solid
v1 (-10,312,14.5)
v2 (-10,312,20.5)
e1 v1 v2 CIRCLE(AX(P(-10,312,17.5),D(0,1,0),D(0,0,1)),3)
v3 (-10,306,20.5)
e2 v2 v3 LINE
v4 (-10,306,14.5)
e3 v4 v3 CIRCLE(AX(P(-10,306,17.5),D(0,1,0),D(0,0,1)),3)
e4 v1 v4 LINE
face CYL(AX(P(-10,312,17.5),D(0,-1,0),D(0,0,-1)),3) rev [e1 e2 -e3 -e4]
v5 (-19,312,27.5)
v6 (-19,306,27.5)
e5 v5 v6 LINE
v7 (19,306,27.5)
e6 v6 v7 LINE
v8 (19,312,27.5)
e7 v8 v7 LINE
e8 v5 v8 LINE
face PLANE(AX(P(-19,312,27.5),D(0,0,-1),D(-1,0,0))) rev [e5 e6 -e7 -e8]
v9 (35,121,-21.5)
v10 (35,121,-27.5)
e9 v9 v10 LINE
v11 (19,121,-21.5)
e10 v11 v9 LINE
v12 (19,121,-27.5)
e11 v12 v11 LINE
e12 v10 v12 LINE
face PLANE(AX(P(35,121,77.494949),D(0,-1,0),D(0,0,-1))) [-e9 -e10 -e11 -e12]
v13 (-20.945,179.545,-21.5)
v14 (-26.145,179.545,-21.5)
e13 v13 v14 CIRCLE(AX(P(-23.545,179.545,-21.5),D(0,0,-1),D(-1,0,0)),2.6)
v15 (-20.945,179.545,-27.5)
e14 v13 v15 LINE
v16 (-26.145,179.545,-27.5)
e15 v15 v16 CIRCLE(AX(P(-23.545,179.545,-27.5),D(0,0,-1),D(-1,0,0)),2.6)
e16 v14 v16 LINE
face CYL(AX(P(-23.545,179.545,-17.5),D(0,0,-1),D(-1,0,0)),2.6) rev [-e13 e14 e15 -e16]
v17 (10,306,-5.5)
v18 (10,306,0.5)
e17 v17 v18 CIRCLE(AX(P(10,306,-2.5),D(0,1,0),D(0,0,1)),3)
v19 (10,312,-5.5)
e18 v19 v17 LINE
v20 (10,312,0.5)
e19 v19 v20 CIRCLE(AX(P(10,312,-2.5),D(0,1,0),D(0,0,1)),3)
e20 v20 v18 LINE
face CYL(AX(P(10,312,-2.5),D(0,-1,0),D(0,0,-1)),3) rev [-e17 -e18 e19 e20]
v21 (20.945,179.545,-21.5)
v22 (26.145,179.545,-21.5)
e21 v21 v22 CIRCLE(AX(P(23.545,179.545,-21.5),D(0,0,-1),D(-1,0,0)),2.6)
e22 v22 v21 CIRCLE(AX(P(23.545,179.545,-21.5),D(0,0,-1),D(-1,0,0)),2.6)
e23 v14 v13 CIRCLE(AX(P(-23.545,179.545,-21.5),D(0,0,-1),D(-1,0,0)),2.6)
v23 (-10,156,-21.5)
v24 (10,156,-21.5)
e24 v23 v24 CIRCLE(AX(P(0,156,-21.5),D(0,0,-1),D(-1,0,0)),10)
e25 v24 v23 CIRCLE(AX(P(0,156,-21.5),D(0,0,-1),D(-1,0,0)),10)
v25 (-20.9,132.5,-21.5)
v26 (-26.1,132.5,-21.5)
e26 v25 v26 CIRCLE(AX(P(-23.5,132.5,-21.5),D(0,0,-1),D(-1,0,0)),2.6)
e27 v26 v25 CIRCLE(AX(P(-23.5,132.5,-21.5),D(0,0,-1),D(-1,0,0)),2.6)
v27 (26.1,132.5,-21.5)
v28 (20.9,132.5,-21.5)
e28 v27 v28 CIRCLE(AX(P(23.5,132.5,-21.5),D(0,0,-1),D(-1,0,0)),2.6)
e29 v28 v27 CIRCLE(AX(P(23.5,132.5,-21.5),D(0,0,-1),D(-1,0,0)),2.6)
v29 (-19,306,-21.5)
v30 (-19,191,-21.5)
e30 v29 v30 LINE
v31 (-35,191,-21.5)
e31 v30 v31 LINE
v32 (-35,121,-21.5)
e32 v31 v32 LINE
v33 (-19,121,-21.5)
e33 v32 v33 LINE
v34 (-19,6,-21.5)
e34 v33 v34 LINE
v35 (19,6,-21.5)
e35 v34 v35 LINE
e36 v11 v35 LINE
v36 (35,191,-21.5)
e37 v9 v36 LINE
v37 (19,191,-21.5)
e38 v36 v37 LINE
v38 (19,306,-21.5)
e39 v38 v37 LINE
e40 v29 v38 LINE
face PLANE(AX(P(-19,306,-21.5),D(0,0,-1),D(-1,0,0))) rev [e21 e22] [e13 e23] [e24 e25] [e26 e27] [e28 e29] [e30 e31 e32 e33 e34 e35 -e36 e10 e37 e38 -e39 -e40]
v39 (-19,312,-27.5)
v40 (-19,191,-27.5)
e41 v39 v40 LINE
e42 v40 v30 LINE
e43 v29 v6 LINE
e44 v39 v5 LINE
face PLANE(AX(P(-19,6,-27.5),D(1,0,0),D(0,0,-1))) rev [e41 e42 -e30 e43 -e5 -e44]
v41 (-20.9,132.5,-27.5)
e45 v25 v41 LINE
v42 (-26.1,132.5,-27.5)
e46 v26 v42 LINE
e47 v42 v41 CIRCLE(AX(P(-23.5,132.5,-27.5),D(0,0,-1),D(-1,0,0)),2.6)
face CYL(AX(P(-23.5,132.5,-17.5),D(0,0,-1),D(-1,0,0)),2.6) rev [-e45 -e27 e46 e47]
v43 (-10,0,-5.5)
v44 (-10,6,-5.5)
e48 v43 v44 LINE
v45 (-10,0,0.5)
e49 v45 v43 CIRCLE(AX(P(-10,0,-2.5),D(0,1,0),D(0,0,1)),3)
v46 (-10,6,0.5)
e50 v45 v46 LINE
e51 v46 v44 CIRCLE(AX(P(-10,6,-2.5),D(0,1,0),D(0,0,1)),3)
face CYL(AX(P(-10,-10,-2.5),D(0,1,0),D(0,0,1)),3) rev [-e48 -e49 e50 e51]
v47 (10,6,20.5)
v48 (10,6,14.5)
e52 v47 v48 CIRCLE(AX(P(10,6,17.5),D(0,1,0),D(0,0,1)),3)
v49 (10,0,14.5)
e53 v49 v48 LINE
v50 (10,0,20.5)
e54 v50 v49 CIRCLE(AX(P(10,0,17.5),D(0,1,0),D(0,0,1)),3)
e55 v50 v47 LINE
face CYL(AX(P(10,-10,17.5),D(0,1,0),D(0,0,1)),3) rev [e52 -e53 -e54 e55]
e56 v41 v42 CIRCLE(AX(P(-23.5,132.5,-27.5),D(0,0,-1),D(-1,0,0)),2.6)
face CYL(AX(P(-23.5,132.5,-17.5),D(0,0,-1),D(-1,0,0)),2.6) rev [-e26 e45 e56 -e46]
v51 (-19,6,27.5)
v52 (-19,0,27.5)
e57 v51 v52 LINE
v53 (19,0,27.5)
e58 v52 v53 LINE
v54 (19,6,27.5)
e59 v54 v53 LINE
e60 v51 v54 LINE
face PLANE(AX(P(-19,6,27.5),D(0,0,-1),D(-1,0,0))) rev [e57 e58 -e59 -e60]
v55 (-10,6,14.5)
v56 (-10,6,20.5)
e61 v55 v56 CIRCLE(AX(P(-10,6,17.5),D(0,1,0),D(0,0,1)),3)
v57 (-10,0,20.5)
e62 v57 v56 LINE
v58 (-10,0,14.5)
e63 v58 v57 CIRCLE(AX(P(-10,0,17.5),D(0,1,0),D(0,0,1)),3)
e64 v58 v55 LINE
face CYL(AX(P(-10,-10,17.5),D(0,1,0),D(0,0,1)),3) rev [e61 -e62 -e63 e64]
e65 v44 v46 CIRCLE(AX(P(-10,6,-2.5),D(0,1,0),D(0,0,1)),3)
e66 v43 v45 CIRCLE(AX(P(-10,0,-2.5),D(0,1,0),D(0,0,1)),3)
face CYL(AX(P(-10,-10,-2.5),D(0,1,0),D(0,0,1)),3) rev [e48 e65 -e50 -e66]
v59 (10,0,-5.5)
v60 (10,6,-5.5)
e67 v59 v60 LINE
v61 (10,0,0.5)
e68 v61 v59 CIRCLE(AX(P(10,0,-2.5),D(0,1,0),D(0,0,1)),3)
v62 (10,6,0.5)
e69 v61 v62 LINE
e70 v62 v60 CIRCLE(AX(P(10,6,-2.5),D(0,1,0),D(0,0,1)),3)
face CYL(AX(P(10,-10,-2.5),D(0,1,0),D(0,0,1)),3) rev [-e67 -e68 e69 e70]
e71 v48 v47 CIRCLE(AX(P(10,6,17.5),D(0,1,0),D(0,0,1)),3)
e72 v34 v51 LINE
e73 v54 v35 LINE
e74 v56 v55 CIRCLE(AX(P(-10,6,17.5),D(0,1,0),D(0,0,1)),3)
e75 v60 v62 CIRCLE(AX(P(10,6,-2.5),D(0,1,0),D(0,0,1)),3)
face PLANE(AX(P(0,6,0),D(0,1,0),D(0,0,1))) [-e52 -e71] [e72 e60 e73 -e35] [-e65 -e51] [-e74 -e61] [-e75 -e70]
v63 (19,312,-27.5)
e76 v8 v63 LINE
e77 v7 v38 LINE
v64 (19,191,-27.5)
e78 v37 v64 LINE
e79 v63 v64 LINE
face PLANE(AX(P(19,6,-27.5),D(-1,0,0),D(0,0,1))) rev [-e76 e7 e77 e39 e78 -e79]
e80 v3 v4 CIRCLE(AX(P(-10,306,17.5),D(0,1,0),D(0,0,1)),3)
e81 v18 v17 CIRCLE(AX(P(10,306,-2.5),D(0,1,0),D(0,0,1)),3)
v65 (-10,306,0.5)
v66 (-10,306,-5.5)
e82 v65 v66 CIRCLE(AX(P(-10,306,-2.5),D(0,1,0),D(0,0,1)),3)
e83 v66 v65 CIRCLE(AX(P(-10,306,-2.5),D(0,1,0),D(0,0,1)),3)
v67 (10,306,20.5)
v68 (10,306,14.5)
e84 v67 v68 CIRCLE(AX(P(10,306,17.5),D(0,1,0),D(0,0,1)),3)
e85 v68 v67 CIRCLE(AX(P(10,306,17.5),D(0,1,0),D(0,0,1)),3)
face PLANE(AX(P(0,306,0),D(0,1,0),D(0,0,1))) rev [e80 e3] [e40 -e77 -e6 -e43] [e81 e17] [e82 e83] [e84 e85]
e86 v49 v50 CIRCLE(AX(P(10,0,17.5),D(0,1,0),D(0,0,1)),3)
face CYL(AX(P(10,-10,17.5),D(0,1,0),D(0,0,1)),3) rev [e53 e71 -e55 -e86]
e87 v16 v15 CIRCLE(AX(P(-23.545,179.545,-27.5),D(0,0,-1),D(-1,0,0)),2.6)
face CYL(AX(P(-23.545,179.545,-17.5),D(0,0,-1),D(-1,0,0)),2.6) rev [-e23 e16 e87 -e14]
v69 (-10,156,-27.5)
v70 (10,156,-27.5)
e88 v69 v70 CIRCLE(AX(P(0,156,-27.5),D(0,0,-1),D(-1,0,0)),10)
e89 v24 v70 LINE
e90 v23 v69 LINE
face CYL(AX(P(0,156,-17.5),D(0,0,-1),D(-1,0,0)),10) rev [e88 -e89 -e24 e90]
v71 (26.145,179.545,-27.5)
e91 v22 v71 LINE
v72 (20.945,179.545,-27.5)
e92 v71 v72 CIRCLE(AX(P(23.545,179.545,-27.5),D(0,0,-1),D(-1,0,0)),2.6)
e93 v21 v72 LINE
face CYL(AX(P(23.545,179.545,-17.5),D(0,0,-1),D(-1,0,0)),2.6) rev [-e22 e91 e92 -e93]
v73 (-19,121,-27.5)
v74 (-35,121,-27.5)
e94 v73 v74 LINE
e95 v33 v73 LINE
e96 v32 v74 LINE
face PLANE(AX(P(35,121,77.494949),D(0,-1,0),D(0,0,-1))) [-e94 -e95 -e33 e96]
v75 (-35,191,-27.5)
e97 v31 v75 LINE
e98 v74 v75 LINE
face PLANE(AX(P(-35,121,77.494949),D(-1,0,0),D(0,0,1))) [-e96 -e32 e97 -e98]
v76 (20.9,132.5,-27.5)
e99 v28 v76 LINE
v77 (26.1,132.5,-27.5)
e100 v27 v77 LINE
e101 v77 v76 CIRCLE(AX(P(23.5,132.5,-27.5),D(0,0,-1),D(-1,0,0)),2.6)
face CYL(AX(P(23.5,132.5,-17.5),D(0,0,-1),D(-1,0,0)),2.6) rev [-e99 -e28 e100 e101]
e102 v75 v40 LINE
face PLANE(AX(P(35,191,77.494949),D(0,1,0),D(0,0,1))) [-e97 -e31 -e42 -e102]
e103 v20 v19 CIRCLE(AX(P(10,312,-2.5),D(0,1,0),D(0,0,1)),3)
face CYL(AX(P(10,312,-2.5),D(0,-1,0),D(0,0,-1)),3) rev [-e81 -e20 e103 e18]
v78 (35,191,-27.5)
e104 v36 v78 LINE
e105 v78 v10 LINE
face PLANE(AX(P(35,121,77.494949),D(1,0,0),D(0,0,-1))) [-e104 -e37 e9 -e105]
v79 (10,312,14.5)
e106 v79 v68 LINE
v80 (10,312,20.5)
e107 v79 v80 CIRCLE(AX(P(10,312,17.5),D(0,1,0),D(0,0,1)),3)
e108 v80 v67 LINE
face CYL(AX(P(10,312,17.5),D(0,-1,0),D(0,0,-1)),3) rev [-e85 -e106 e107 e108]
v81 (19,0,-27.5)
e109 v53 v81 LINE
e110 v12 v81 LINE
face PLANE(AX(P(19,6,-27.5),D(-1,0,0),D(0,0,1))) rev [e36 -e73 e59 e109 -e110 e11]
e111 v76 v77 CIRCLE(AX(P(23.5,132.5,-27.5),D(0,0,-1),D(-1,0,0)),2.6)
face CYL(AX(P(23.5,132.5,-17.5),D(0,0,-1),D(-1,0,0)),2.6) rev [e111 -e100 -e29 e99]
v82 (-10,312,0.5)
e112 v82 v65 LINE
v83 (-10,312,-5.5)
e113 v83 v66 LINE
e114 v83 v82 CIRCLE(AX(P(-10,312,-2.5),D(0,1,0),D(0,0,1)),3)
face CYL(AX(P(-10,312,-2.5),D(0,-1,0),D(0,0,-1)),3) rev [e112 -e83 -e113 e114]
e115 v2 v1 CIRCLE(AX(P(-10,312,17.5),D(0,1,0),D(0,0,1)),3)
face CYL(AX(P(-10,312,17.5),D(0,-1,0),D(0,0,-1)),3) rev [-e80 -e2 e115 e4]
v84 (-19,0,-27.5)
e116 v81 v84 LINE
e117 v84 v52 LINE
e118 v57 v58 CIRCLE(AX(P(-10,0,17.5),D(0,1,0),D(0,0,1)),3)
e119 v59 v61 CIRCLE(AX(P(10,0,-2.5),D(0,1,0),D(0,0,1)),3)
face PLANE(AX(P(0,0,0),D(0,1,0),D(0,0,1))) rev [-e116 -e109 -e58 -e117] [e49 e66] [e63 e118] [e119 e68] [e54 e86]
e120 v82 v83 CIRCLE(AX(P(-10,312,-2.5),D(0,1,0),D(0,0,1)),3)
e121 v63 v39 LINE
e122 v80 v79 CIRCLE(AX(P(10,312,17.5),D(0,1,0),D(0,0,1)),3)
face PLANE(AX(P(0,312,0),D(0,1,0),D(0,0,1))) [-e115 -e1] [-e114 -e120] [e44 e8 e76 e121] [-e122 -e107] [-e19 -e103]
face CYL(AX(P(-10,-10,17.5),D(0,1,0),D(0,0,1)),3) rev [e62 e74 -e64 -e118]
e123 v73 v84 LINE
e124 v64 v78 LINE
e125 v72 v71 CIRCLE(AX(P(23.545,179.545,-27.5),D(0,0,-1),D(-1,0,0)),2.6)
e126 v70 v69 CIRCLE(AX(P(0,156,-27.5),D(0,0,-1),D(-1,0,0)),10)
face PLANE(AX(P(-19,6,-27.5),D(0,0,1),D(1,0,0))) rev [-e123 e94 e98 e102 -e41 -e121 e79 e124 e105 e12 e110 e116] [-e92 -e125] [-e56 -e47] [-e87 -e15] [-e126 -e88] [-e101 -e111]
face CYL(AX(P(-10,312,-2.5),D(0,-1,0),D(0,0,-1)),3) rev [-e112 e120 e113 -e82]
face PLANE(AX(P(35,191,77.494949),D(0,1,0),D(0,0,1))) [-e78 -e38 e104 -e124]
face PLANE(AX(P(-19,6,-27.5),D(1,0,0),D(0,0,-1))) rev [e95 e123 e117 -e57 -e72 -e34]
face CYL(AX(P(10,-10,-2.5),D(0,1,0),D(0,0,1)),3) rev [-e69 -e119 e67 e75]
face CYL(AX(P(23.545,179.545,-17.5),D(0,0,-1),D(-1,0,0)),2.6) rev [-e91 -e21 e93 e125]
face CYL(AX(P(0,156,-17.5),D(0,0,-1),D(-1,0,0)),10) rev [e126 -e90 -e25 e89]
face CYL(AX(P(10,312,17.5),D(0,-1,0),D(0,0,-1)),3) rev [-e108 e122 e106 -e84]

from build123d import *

# Parameters (mm, degrees)
SKETCH_1_W          = 38
SKETCH_1_H          = 55
EXTRUDE_1_DEPTH     = 6
SKETCH_2_R          = 3
CUT_EXTRUDE_1_DEPTH = 16
SKETCH_3_W          = 38
SKETCH_3_H          = 6
EXTRUDE_2_DEPTH     = 300
EXTRUDE_START       = 6
SKETCH_5_R          = 3
EXTRUDE_3_DEPTH     = 6
SKETCH_6_W          = 70
SKETCH_6_H          = 70
EXTRUDE_4_DEPTH     = 6
SKETCH_7_R          = 2.6
SKETCH_7_R_2        = 10
CUT_EXTRUDE_2_DEPTH = 10


with BuildPart() as part:
    # 草图1 → 凸台-拉伸1 (new body)
    with BuildSketch(Plane(origin=(0, 0, 0), x_dir=(1, 0, 0), z_dir=(0, 1, 0))):
        Rectangle(SKETCH_1_W, SKETCH_1_H)
    extrude(amount=EXTRUDE_1_DEPTH)

    # 草图2 → 切除-拉伸1 (cut)
    with BuildSketch(Plane(origin=(0, 6, 0), x_dir=(1, 0, 0), z_dir=(0, 1, 0))):
        with Locations(Location((-10, 2.5, 0), (0, 0, 270))):
            Circle(SKETCH_2_R)
        with Locations(Location((10, 2.5, 0), (0, 0, 270))):
            Circle(SKETCH_2_R)
        with Locations(Location((10, -17.5, 0), (0, 0, 270))):
            Circle(SKETCH_2_R)
        with Locations(Location((-10, -17.5, 0), (0, 0, 270))):
            Circle(SKETCH_2_R)
    extrude(amount=-CUT_EXTRUDE_1_DEPTH, mode=Mode.SUBTRACT)

    # 草图3 → 凸台-拉伸2 (add)
    with BuildSketch(Plane(origin=(0, 6, 0), x_dir=(1, 0, 0), z_dir=(0, 1, 0))):
        with Locations((0, 24.5)):
            Rectangle(SKETCH_3_W, SKETCH_3_H)
    extrude(amount=EXTRUDE_2_DEPTH)

    # 草图5 → 凸台-拉伸3 (add)
    with BuildSketch(Plane(origin=(0, 306, 0), x_dir=(1, 0, 0), z_dir=(0, 1, 0)).offset(EXTRUDE_START)):
        Polygon((-19, 27.5), (-19, 21.5), (-19, -27.5), (19, -27.5), (19, 21.5), (19, 27.5), align=None)
        with Locations(Location((-10, 2.5, 0), (0, 0, 270))):
            Circle(SKETCH_5_R, mode=Mode.SUBTRACT)
        with Locations(Location((10, 2.5, 0), (0, 0, 270))):
            Circle(SKETCH_5_R, mode=Mode.SUBTRACT)
        with Locations(Location((-10, -17.5, 0), (0, 0, 270))):
            Circle(SKETCH_5_R, mode=Mode.SUBTRACT)
        with Locations(Location((10, -17.5, 0), (0, 0, 270))):
            Circle(SKETCH_5_R, mode=Mode.SUBTRACT)
    extrude(amount=-EXTRUDE_3_DEPTH)

    # 草图6 → 凸台-拉伸4 (add)
    with BuildSketch(Plane(origin=(0, 0, -27.5), x_dir=(-1, 0, 0), z_dir=(0, 0, -1))):
        with Locations((0, 156)):
            Rectangle(SKETCH_6_W, SKETCH_6_H)
    extrude(amount=-EXTRUDE_4_DEPTH)

    # 草图7 → 切除-拉伸2 (cut)
    with BuildSketch(Plane(origin=(0, 0, -27.5), x_dir=(-1, 0, 0), z_dir=(0, 0, -1))):
        with Locations((23.545, 179.545)):
            Circle(SKETCH_7_R)
        with Locations((23.5, 132.5)):
            Circle(SKETCH_7_R)
        with Locations((-23.5, 132.5)):
            Circle(SKETCH_7_R)
        with Locations((-23.545, 179.545)):
            Circle(SKETCH_7_R)
        with Locations((0, 156)):
            Circle(SKETCH_7_R_2)
    extrude(amount=-CUT_EXTRUDE_2_DEPTH, mode=Mode.SUBTRACT)


solid = part.part
